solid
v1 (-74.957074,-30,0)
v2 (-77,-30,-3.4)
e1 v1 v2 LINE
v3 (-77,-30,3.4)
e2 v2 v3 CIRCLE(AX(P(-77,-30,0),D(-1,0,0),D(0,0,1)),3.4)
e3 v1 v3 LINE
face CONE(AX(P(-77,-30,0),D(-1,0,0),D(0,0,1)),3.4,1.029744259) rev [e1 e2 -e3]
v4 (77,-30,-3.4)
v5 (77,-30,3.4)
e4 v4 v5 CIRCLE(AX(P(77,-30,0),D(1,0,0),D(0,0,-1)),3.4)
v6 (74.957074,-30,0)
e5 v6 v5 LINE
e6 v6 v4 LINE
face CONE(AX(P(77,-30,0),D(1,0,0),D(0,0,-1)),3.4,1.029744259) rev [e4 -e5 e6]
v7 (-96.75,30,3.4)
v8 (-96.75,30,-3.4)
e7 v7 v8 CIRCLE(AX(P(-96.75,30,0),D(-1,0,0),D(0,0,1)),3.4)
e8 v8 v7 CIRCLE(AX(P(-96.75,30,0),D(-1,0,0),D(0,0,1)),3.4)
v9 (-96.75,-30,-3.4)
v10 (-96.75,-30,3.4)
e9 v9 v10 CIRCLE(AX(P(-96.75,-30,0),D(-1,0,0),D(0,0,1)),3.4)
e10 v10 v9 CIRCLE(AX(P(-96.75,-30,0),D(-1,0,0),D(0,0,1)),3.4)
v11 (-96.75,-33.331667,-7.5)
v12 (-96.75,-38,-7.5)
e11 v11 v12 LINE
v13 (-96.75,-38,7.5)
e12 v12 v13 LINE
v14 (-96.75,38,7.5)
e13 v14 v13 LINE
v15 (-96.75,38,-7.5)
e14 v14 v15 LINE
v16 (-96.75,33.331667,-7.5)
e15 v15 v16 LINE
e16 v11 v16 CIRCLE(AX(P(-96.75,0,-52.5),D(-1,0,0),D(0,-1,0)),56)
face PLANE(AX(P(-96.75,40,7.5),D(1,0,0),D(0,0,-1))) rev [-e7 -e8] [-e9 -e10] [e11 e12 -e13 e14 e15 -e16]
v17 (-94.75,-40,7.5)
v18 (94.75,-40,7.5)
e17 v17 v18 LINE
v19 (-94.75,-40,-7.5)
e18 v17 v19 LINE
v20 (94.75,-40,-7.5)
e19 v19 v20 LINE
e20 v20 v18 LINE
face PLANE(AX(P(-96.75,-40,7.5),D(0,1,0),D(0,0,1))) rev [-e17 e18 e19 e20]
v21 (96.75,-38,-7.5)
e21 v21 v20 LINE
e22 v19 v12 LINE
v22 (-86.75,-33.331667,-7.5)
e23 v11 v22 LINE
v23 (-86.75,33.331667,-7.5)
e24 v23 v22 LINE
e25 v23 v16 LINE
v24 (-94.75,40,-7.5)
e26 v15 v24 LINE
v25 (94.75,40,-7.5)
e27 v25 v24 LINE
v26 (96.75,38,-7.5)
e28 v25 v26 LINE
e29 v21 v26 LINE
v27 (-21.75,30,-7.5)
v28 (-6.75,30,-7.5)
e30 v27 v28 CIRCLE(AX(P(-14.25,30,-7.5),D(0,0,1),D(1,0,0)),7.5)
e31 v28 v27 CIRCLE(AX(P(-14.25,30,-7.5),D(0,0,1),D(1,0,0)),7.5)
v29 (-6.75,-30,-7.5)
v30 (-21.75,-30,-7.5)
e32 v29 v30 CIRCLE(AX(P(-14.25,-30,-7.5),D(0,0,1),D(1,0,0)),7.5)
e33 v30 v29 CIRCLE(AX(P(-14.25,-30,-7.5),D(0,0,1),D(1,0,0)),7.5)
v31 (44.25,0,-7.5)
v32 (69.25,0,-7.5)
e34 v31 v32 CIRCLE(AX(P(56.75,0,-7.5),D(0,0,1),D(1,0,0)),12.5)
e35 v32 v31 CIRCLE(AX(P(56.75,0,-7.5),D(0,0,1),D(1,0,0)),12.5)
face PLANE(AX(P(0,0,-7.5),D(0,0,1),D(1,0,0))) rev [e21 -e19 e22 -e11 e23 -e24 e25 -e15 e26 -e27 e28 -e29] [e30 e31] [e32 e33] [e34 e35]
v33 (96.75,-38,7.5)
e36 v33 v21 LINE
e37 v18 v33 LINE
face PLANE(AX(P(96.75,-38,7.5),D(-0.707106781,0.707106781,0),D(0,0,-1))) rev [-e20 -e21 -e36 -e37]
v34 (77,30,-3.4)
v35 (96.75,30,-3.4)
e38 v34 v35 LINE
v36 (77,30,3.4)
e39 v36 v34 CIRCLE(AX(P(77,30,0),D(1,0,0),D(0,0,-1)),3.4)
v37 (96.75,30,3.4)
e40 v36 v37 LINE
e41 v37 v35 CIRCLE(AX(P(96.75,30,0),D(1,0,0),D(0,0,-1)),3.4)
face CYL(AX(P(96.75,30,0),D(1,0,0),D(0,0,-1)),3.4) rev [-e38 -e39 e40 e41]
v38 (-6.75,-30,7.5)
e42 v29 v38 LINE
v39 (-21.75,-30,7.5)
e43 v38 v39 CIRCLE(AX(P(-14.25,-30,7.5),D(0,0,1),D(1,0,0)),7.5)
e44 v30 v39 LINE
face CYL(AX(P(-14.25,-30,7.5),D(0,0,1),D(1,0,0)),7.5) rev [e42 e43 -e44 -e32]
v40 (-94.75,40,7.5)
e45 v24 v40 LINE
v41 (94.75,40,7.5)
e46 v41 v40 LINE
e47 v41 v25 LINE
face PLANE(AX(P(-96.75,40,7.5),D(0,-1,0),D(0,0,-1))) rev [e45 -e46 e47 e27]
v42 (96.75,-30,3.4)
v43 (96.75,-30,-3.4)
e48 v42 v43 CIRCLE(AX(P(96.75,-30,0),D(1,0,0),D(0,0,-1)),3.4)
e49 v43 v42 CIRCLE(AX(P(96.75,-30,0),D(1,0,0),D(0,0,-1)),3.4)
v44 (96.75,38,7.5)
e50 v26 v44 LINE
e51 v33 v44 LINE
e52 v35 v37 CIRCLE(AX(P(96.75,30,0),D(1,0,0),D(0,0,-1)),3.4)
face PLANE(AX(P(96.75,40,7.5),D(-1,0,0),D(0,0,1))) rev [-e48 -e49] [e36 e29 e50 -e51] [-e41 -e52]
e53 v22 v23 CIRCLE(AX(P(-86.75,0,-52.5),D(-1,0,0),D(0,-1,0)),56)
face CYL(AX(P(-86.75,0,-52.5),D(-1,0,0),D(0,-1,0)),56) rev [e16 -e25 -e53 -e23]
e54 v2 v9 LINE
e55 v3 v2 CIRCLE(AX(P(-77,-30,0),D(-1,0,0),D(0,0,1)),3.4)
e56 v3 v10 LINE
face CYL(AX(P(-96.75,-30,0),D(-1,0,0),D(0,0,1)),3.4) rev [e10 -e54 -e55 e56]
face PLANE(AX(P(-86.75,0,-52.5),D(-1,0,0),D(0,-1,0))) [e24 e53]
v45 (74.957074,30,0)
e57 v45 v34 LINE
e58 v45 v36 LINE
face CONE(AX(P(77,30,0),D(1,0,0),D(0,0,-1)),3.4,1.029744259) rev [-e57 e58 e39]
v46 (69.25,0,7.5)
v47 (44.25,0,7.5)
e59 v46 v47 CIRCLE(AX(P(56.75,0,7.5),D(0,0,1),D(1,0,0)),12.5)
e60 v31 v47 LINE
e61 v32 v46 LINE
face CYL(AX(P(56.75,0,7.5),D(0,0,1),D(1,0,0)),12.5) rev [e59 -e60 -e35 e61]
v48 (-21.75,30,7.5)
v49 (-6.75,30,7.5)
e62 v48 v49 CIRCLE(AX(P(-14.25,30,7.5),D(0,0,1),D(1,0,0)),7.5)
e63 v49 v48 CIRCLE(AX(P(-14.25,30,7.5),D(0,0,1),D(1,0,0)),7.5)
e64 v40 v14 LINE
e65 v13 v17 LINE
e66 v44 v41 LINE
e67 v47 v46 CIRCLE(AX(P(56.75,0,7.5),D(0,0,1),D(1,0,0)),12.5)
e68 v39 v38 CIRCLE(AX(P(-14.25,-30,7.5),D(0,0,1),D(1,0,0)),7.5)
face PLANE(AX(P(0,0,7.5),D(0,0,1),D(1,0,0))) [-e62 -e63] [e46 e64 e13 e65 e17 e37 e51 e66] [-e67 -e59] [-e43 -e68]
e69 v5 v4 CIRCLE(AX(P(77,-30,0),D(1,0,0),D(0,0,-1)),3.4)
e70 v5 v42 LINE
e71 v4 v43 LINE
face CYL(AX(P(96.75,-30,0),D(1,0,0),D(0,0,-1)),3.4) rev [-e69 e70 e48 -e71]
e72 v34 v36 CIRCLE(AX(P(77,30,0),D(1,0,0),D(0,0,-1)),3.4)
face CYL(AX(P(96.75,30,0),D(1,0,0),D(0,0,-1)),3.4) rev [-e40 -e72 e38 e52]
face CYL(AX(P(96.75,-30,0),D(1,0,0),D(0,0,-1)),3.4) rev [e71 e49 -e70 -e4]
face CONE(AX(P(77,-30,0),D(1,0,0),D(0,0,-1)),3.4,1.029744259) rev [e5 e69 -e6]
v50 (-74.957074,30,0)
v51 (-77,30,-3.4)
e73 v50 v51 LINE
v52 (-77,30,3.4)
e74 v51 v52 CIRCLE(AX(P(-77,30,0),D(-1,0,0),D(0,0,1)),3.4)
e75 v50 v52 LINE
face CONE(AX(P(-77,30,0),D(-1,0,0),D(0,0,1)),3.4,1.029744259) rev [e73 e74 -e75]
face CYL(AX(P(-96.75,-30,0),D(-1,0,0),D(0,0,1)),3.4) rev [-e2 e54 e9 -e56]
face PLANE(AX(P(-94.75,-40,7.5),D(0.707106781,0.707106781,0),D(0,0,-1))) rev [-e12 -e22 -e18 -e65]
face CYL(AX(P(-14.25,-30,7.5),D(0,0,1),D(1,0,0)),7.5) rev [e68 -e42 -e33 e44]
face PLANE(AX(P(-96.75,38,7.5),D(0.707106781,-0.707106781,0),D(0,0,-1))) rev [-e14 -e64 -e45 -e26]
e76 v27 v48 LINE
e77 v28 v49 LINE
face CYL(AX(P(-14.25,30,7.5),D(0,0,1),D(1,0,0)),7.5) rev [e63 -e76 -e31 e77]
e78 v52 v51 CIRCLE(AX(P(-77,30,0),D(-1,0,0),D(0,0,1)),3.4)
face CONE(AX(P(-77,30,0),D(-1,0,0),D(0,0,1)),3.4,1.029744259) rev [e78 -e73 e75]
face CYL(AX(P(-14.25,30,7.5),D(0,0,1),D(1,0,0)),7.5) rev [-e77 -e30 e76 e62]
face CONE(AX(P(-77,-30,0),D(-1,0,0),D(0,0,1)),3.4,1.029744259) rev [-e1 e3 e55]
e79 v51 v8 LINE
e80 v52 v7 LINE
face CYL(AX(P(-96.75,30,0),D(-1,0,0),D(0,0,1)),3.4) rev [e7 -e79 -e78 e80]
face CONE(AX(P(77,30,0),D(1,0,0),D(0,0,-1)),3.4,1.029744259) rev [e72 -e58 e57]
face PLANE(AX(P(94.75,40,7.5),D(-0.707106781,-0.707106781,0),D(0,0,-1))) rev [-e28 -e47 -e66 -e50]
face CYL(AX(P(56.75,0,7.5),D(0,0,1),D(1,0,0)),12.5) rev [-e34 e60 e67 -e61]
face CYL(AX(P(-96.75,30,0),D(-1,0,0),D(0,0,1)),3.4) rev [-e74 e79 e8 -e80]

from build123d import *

# Parameters (mm, degrees)
SKETCH_1_W              = 193.5
SKETCH_1_H              = 80
EXTRUDE_1_DEPTH         = 7.5
HOLE_WIZARD_25_0_25_1_D = 25
HOLE_WIZARD_15_0_15_1_D = 15
HOLE_WIZARD_M8_1_D      = 6.8
HOLE_WIZARD_M8_1_DEPTH  = 19.75
HOLE_WIZARD_M8_1_TIP    = 2.042926105
HOLE_WIZARD_M8_2_D      = 6.8
HOLE_WIZARD_M8_2_DEPTH  = 19.75
HOLE_WIZARD_M8_2_TIP    = 2.042926105
SKETCH_11_R             = 56
CUT_EXTRUDE_1_DEPTH     = 10
CHAMFER_1_SIZE          = 2


with BuildPart() as part:
    # 草图1 → 凸台-拉伸1 (new, symmetric)
    with BuildSketch(Plane.XY):
        Rectangle(SKETCH_1_W, SKETCH_1_H)
    extrude(amount=EXTRUDE_1_DEPTH, both=True)

    # Ø25.0 (25) 直径孔1 (through all)
    with Locations(Plane.XY.offset(7.5)):
        with Locations((56.75, 0)):
            Hole(HOLE_WIZARD_25_0_25_1_D / 2)

    # Ø15.0 (15) 直径孔1 (through all)
    with Locations(Plane.XY.offset(7.5)):
        with Locations((-14.25, 30), (-14.25, -30)):
            Hole(HOLE_WIZARD_15_0_15_1_D / 2)

    # M8 螺纹孔1
    with Locations(Plane(origin=(96.75, 0, 0), x_dir=(0, 0, -1), z_dir=(1, 0, 0))):
        with Locations((0, 30), (0, -30)):
            Hole(HOLE_WIZARD_M8_1_D / 2, depth=HOLE_WIZARD_M8_1_DEPTH)
            with Locations((0, 0, -(HOLE_WIZARD_M8_1_DEPTH + HOLE_WIZARD_M8_1_TIP / 2))):  # 118° drill point
                Cone(0, HOLE_WIZARD_M8_1_D / 2, HOLE_WIZARD_M8_1_TIP, mode=Mode.SUBTRACT)

    # M8 螺纹孔2
    with Locations(Plane.ZY.offset(96.75)):
        with Locations((0, 30), (0, -30)):
            Hole(HOLE_WIZARD_M8_2_D / 2, depth=HOLE_WIZARD_M8_2_DEPTH)
            with Locations((0, 0, -(HOLE_WIZARD_M8_2_DEPTH + HOLE_WIZARD_M8_2_TIP / 2))):  # 118° drill point
                Cone(0, HOLE_WIZARD_M8_2_D / 2, HOLE_WIZARD_M8_2_TIP, mode=Mode.SUBTRACT)

    # 草图11 → 切除-拉伸1 (cut)
    with BuildSketch(Plane.ZY.offset(96.75)):
        with Locations((-52.5, 0)):
            Circle(SKETCH_11_R)
    extrude(amount=-CUT_EXTRUDE_1_DEPTH, mode=Mode.SUBTRACT)

    # 倒角1
    chamfer_1_edges = [part.edges().sort_by_distance(p)[0] for p in [
        (96.75, -40, 0),
        (-96.75, -40, 0),
        (-96.75, 40, 0),
        (96.75, 40, 0),
    ]]
    chamfer(chamfer_1_edges, length=CHAMFER_1_SIZE)


solid = part.part
